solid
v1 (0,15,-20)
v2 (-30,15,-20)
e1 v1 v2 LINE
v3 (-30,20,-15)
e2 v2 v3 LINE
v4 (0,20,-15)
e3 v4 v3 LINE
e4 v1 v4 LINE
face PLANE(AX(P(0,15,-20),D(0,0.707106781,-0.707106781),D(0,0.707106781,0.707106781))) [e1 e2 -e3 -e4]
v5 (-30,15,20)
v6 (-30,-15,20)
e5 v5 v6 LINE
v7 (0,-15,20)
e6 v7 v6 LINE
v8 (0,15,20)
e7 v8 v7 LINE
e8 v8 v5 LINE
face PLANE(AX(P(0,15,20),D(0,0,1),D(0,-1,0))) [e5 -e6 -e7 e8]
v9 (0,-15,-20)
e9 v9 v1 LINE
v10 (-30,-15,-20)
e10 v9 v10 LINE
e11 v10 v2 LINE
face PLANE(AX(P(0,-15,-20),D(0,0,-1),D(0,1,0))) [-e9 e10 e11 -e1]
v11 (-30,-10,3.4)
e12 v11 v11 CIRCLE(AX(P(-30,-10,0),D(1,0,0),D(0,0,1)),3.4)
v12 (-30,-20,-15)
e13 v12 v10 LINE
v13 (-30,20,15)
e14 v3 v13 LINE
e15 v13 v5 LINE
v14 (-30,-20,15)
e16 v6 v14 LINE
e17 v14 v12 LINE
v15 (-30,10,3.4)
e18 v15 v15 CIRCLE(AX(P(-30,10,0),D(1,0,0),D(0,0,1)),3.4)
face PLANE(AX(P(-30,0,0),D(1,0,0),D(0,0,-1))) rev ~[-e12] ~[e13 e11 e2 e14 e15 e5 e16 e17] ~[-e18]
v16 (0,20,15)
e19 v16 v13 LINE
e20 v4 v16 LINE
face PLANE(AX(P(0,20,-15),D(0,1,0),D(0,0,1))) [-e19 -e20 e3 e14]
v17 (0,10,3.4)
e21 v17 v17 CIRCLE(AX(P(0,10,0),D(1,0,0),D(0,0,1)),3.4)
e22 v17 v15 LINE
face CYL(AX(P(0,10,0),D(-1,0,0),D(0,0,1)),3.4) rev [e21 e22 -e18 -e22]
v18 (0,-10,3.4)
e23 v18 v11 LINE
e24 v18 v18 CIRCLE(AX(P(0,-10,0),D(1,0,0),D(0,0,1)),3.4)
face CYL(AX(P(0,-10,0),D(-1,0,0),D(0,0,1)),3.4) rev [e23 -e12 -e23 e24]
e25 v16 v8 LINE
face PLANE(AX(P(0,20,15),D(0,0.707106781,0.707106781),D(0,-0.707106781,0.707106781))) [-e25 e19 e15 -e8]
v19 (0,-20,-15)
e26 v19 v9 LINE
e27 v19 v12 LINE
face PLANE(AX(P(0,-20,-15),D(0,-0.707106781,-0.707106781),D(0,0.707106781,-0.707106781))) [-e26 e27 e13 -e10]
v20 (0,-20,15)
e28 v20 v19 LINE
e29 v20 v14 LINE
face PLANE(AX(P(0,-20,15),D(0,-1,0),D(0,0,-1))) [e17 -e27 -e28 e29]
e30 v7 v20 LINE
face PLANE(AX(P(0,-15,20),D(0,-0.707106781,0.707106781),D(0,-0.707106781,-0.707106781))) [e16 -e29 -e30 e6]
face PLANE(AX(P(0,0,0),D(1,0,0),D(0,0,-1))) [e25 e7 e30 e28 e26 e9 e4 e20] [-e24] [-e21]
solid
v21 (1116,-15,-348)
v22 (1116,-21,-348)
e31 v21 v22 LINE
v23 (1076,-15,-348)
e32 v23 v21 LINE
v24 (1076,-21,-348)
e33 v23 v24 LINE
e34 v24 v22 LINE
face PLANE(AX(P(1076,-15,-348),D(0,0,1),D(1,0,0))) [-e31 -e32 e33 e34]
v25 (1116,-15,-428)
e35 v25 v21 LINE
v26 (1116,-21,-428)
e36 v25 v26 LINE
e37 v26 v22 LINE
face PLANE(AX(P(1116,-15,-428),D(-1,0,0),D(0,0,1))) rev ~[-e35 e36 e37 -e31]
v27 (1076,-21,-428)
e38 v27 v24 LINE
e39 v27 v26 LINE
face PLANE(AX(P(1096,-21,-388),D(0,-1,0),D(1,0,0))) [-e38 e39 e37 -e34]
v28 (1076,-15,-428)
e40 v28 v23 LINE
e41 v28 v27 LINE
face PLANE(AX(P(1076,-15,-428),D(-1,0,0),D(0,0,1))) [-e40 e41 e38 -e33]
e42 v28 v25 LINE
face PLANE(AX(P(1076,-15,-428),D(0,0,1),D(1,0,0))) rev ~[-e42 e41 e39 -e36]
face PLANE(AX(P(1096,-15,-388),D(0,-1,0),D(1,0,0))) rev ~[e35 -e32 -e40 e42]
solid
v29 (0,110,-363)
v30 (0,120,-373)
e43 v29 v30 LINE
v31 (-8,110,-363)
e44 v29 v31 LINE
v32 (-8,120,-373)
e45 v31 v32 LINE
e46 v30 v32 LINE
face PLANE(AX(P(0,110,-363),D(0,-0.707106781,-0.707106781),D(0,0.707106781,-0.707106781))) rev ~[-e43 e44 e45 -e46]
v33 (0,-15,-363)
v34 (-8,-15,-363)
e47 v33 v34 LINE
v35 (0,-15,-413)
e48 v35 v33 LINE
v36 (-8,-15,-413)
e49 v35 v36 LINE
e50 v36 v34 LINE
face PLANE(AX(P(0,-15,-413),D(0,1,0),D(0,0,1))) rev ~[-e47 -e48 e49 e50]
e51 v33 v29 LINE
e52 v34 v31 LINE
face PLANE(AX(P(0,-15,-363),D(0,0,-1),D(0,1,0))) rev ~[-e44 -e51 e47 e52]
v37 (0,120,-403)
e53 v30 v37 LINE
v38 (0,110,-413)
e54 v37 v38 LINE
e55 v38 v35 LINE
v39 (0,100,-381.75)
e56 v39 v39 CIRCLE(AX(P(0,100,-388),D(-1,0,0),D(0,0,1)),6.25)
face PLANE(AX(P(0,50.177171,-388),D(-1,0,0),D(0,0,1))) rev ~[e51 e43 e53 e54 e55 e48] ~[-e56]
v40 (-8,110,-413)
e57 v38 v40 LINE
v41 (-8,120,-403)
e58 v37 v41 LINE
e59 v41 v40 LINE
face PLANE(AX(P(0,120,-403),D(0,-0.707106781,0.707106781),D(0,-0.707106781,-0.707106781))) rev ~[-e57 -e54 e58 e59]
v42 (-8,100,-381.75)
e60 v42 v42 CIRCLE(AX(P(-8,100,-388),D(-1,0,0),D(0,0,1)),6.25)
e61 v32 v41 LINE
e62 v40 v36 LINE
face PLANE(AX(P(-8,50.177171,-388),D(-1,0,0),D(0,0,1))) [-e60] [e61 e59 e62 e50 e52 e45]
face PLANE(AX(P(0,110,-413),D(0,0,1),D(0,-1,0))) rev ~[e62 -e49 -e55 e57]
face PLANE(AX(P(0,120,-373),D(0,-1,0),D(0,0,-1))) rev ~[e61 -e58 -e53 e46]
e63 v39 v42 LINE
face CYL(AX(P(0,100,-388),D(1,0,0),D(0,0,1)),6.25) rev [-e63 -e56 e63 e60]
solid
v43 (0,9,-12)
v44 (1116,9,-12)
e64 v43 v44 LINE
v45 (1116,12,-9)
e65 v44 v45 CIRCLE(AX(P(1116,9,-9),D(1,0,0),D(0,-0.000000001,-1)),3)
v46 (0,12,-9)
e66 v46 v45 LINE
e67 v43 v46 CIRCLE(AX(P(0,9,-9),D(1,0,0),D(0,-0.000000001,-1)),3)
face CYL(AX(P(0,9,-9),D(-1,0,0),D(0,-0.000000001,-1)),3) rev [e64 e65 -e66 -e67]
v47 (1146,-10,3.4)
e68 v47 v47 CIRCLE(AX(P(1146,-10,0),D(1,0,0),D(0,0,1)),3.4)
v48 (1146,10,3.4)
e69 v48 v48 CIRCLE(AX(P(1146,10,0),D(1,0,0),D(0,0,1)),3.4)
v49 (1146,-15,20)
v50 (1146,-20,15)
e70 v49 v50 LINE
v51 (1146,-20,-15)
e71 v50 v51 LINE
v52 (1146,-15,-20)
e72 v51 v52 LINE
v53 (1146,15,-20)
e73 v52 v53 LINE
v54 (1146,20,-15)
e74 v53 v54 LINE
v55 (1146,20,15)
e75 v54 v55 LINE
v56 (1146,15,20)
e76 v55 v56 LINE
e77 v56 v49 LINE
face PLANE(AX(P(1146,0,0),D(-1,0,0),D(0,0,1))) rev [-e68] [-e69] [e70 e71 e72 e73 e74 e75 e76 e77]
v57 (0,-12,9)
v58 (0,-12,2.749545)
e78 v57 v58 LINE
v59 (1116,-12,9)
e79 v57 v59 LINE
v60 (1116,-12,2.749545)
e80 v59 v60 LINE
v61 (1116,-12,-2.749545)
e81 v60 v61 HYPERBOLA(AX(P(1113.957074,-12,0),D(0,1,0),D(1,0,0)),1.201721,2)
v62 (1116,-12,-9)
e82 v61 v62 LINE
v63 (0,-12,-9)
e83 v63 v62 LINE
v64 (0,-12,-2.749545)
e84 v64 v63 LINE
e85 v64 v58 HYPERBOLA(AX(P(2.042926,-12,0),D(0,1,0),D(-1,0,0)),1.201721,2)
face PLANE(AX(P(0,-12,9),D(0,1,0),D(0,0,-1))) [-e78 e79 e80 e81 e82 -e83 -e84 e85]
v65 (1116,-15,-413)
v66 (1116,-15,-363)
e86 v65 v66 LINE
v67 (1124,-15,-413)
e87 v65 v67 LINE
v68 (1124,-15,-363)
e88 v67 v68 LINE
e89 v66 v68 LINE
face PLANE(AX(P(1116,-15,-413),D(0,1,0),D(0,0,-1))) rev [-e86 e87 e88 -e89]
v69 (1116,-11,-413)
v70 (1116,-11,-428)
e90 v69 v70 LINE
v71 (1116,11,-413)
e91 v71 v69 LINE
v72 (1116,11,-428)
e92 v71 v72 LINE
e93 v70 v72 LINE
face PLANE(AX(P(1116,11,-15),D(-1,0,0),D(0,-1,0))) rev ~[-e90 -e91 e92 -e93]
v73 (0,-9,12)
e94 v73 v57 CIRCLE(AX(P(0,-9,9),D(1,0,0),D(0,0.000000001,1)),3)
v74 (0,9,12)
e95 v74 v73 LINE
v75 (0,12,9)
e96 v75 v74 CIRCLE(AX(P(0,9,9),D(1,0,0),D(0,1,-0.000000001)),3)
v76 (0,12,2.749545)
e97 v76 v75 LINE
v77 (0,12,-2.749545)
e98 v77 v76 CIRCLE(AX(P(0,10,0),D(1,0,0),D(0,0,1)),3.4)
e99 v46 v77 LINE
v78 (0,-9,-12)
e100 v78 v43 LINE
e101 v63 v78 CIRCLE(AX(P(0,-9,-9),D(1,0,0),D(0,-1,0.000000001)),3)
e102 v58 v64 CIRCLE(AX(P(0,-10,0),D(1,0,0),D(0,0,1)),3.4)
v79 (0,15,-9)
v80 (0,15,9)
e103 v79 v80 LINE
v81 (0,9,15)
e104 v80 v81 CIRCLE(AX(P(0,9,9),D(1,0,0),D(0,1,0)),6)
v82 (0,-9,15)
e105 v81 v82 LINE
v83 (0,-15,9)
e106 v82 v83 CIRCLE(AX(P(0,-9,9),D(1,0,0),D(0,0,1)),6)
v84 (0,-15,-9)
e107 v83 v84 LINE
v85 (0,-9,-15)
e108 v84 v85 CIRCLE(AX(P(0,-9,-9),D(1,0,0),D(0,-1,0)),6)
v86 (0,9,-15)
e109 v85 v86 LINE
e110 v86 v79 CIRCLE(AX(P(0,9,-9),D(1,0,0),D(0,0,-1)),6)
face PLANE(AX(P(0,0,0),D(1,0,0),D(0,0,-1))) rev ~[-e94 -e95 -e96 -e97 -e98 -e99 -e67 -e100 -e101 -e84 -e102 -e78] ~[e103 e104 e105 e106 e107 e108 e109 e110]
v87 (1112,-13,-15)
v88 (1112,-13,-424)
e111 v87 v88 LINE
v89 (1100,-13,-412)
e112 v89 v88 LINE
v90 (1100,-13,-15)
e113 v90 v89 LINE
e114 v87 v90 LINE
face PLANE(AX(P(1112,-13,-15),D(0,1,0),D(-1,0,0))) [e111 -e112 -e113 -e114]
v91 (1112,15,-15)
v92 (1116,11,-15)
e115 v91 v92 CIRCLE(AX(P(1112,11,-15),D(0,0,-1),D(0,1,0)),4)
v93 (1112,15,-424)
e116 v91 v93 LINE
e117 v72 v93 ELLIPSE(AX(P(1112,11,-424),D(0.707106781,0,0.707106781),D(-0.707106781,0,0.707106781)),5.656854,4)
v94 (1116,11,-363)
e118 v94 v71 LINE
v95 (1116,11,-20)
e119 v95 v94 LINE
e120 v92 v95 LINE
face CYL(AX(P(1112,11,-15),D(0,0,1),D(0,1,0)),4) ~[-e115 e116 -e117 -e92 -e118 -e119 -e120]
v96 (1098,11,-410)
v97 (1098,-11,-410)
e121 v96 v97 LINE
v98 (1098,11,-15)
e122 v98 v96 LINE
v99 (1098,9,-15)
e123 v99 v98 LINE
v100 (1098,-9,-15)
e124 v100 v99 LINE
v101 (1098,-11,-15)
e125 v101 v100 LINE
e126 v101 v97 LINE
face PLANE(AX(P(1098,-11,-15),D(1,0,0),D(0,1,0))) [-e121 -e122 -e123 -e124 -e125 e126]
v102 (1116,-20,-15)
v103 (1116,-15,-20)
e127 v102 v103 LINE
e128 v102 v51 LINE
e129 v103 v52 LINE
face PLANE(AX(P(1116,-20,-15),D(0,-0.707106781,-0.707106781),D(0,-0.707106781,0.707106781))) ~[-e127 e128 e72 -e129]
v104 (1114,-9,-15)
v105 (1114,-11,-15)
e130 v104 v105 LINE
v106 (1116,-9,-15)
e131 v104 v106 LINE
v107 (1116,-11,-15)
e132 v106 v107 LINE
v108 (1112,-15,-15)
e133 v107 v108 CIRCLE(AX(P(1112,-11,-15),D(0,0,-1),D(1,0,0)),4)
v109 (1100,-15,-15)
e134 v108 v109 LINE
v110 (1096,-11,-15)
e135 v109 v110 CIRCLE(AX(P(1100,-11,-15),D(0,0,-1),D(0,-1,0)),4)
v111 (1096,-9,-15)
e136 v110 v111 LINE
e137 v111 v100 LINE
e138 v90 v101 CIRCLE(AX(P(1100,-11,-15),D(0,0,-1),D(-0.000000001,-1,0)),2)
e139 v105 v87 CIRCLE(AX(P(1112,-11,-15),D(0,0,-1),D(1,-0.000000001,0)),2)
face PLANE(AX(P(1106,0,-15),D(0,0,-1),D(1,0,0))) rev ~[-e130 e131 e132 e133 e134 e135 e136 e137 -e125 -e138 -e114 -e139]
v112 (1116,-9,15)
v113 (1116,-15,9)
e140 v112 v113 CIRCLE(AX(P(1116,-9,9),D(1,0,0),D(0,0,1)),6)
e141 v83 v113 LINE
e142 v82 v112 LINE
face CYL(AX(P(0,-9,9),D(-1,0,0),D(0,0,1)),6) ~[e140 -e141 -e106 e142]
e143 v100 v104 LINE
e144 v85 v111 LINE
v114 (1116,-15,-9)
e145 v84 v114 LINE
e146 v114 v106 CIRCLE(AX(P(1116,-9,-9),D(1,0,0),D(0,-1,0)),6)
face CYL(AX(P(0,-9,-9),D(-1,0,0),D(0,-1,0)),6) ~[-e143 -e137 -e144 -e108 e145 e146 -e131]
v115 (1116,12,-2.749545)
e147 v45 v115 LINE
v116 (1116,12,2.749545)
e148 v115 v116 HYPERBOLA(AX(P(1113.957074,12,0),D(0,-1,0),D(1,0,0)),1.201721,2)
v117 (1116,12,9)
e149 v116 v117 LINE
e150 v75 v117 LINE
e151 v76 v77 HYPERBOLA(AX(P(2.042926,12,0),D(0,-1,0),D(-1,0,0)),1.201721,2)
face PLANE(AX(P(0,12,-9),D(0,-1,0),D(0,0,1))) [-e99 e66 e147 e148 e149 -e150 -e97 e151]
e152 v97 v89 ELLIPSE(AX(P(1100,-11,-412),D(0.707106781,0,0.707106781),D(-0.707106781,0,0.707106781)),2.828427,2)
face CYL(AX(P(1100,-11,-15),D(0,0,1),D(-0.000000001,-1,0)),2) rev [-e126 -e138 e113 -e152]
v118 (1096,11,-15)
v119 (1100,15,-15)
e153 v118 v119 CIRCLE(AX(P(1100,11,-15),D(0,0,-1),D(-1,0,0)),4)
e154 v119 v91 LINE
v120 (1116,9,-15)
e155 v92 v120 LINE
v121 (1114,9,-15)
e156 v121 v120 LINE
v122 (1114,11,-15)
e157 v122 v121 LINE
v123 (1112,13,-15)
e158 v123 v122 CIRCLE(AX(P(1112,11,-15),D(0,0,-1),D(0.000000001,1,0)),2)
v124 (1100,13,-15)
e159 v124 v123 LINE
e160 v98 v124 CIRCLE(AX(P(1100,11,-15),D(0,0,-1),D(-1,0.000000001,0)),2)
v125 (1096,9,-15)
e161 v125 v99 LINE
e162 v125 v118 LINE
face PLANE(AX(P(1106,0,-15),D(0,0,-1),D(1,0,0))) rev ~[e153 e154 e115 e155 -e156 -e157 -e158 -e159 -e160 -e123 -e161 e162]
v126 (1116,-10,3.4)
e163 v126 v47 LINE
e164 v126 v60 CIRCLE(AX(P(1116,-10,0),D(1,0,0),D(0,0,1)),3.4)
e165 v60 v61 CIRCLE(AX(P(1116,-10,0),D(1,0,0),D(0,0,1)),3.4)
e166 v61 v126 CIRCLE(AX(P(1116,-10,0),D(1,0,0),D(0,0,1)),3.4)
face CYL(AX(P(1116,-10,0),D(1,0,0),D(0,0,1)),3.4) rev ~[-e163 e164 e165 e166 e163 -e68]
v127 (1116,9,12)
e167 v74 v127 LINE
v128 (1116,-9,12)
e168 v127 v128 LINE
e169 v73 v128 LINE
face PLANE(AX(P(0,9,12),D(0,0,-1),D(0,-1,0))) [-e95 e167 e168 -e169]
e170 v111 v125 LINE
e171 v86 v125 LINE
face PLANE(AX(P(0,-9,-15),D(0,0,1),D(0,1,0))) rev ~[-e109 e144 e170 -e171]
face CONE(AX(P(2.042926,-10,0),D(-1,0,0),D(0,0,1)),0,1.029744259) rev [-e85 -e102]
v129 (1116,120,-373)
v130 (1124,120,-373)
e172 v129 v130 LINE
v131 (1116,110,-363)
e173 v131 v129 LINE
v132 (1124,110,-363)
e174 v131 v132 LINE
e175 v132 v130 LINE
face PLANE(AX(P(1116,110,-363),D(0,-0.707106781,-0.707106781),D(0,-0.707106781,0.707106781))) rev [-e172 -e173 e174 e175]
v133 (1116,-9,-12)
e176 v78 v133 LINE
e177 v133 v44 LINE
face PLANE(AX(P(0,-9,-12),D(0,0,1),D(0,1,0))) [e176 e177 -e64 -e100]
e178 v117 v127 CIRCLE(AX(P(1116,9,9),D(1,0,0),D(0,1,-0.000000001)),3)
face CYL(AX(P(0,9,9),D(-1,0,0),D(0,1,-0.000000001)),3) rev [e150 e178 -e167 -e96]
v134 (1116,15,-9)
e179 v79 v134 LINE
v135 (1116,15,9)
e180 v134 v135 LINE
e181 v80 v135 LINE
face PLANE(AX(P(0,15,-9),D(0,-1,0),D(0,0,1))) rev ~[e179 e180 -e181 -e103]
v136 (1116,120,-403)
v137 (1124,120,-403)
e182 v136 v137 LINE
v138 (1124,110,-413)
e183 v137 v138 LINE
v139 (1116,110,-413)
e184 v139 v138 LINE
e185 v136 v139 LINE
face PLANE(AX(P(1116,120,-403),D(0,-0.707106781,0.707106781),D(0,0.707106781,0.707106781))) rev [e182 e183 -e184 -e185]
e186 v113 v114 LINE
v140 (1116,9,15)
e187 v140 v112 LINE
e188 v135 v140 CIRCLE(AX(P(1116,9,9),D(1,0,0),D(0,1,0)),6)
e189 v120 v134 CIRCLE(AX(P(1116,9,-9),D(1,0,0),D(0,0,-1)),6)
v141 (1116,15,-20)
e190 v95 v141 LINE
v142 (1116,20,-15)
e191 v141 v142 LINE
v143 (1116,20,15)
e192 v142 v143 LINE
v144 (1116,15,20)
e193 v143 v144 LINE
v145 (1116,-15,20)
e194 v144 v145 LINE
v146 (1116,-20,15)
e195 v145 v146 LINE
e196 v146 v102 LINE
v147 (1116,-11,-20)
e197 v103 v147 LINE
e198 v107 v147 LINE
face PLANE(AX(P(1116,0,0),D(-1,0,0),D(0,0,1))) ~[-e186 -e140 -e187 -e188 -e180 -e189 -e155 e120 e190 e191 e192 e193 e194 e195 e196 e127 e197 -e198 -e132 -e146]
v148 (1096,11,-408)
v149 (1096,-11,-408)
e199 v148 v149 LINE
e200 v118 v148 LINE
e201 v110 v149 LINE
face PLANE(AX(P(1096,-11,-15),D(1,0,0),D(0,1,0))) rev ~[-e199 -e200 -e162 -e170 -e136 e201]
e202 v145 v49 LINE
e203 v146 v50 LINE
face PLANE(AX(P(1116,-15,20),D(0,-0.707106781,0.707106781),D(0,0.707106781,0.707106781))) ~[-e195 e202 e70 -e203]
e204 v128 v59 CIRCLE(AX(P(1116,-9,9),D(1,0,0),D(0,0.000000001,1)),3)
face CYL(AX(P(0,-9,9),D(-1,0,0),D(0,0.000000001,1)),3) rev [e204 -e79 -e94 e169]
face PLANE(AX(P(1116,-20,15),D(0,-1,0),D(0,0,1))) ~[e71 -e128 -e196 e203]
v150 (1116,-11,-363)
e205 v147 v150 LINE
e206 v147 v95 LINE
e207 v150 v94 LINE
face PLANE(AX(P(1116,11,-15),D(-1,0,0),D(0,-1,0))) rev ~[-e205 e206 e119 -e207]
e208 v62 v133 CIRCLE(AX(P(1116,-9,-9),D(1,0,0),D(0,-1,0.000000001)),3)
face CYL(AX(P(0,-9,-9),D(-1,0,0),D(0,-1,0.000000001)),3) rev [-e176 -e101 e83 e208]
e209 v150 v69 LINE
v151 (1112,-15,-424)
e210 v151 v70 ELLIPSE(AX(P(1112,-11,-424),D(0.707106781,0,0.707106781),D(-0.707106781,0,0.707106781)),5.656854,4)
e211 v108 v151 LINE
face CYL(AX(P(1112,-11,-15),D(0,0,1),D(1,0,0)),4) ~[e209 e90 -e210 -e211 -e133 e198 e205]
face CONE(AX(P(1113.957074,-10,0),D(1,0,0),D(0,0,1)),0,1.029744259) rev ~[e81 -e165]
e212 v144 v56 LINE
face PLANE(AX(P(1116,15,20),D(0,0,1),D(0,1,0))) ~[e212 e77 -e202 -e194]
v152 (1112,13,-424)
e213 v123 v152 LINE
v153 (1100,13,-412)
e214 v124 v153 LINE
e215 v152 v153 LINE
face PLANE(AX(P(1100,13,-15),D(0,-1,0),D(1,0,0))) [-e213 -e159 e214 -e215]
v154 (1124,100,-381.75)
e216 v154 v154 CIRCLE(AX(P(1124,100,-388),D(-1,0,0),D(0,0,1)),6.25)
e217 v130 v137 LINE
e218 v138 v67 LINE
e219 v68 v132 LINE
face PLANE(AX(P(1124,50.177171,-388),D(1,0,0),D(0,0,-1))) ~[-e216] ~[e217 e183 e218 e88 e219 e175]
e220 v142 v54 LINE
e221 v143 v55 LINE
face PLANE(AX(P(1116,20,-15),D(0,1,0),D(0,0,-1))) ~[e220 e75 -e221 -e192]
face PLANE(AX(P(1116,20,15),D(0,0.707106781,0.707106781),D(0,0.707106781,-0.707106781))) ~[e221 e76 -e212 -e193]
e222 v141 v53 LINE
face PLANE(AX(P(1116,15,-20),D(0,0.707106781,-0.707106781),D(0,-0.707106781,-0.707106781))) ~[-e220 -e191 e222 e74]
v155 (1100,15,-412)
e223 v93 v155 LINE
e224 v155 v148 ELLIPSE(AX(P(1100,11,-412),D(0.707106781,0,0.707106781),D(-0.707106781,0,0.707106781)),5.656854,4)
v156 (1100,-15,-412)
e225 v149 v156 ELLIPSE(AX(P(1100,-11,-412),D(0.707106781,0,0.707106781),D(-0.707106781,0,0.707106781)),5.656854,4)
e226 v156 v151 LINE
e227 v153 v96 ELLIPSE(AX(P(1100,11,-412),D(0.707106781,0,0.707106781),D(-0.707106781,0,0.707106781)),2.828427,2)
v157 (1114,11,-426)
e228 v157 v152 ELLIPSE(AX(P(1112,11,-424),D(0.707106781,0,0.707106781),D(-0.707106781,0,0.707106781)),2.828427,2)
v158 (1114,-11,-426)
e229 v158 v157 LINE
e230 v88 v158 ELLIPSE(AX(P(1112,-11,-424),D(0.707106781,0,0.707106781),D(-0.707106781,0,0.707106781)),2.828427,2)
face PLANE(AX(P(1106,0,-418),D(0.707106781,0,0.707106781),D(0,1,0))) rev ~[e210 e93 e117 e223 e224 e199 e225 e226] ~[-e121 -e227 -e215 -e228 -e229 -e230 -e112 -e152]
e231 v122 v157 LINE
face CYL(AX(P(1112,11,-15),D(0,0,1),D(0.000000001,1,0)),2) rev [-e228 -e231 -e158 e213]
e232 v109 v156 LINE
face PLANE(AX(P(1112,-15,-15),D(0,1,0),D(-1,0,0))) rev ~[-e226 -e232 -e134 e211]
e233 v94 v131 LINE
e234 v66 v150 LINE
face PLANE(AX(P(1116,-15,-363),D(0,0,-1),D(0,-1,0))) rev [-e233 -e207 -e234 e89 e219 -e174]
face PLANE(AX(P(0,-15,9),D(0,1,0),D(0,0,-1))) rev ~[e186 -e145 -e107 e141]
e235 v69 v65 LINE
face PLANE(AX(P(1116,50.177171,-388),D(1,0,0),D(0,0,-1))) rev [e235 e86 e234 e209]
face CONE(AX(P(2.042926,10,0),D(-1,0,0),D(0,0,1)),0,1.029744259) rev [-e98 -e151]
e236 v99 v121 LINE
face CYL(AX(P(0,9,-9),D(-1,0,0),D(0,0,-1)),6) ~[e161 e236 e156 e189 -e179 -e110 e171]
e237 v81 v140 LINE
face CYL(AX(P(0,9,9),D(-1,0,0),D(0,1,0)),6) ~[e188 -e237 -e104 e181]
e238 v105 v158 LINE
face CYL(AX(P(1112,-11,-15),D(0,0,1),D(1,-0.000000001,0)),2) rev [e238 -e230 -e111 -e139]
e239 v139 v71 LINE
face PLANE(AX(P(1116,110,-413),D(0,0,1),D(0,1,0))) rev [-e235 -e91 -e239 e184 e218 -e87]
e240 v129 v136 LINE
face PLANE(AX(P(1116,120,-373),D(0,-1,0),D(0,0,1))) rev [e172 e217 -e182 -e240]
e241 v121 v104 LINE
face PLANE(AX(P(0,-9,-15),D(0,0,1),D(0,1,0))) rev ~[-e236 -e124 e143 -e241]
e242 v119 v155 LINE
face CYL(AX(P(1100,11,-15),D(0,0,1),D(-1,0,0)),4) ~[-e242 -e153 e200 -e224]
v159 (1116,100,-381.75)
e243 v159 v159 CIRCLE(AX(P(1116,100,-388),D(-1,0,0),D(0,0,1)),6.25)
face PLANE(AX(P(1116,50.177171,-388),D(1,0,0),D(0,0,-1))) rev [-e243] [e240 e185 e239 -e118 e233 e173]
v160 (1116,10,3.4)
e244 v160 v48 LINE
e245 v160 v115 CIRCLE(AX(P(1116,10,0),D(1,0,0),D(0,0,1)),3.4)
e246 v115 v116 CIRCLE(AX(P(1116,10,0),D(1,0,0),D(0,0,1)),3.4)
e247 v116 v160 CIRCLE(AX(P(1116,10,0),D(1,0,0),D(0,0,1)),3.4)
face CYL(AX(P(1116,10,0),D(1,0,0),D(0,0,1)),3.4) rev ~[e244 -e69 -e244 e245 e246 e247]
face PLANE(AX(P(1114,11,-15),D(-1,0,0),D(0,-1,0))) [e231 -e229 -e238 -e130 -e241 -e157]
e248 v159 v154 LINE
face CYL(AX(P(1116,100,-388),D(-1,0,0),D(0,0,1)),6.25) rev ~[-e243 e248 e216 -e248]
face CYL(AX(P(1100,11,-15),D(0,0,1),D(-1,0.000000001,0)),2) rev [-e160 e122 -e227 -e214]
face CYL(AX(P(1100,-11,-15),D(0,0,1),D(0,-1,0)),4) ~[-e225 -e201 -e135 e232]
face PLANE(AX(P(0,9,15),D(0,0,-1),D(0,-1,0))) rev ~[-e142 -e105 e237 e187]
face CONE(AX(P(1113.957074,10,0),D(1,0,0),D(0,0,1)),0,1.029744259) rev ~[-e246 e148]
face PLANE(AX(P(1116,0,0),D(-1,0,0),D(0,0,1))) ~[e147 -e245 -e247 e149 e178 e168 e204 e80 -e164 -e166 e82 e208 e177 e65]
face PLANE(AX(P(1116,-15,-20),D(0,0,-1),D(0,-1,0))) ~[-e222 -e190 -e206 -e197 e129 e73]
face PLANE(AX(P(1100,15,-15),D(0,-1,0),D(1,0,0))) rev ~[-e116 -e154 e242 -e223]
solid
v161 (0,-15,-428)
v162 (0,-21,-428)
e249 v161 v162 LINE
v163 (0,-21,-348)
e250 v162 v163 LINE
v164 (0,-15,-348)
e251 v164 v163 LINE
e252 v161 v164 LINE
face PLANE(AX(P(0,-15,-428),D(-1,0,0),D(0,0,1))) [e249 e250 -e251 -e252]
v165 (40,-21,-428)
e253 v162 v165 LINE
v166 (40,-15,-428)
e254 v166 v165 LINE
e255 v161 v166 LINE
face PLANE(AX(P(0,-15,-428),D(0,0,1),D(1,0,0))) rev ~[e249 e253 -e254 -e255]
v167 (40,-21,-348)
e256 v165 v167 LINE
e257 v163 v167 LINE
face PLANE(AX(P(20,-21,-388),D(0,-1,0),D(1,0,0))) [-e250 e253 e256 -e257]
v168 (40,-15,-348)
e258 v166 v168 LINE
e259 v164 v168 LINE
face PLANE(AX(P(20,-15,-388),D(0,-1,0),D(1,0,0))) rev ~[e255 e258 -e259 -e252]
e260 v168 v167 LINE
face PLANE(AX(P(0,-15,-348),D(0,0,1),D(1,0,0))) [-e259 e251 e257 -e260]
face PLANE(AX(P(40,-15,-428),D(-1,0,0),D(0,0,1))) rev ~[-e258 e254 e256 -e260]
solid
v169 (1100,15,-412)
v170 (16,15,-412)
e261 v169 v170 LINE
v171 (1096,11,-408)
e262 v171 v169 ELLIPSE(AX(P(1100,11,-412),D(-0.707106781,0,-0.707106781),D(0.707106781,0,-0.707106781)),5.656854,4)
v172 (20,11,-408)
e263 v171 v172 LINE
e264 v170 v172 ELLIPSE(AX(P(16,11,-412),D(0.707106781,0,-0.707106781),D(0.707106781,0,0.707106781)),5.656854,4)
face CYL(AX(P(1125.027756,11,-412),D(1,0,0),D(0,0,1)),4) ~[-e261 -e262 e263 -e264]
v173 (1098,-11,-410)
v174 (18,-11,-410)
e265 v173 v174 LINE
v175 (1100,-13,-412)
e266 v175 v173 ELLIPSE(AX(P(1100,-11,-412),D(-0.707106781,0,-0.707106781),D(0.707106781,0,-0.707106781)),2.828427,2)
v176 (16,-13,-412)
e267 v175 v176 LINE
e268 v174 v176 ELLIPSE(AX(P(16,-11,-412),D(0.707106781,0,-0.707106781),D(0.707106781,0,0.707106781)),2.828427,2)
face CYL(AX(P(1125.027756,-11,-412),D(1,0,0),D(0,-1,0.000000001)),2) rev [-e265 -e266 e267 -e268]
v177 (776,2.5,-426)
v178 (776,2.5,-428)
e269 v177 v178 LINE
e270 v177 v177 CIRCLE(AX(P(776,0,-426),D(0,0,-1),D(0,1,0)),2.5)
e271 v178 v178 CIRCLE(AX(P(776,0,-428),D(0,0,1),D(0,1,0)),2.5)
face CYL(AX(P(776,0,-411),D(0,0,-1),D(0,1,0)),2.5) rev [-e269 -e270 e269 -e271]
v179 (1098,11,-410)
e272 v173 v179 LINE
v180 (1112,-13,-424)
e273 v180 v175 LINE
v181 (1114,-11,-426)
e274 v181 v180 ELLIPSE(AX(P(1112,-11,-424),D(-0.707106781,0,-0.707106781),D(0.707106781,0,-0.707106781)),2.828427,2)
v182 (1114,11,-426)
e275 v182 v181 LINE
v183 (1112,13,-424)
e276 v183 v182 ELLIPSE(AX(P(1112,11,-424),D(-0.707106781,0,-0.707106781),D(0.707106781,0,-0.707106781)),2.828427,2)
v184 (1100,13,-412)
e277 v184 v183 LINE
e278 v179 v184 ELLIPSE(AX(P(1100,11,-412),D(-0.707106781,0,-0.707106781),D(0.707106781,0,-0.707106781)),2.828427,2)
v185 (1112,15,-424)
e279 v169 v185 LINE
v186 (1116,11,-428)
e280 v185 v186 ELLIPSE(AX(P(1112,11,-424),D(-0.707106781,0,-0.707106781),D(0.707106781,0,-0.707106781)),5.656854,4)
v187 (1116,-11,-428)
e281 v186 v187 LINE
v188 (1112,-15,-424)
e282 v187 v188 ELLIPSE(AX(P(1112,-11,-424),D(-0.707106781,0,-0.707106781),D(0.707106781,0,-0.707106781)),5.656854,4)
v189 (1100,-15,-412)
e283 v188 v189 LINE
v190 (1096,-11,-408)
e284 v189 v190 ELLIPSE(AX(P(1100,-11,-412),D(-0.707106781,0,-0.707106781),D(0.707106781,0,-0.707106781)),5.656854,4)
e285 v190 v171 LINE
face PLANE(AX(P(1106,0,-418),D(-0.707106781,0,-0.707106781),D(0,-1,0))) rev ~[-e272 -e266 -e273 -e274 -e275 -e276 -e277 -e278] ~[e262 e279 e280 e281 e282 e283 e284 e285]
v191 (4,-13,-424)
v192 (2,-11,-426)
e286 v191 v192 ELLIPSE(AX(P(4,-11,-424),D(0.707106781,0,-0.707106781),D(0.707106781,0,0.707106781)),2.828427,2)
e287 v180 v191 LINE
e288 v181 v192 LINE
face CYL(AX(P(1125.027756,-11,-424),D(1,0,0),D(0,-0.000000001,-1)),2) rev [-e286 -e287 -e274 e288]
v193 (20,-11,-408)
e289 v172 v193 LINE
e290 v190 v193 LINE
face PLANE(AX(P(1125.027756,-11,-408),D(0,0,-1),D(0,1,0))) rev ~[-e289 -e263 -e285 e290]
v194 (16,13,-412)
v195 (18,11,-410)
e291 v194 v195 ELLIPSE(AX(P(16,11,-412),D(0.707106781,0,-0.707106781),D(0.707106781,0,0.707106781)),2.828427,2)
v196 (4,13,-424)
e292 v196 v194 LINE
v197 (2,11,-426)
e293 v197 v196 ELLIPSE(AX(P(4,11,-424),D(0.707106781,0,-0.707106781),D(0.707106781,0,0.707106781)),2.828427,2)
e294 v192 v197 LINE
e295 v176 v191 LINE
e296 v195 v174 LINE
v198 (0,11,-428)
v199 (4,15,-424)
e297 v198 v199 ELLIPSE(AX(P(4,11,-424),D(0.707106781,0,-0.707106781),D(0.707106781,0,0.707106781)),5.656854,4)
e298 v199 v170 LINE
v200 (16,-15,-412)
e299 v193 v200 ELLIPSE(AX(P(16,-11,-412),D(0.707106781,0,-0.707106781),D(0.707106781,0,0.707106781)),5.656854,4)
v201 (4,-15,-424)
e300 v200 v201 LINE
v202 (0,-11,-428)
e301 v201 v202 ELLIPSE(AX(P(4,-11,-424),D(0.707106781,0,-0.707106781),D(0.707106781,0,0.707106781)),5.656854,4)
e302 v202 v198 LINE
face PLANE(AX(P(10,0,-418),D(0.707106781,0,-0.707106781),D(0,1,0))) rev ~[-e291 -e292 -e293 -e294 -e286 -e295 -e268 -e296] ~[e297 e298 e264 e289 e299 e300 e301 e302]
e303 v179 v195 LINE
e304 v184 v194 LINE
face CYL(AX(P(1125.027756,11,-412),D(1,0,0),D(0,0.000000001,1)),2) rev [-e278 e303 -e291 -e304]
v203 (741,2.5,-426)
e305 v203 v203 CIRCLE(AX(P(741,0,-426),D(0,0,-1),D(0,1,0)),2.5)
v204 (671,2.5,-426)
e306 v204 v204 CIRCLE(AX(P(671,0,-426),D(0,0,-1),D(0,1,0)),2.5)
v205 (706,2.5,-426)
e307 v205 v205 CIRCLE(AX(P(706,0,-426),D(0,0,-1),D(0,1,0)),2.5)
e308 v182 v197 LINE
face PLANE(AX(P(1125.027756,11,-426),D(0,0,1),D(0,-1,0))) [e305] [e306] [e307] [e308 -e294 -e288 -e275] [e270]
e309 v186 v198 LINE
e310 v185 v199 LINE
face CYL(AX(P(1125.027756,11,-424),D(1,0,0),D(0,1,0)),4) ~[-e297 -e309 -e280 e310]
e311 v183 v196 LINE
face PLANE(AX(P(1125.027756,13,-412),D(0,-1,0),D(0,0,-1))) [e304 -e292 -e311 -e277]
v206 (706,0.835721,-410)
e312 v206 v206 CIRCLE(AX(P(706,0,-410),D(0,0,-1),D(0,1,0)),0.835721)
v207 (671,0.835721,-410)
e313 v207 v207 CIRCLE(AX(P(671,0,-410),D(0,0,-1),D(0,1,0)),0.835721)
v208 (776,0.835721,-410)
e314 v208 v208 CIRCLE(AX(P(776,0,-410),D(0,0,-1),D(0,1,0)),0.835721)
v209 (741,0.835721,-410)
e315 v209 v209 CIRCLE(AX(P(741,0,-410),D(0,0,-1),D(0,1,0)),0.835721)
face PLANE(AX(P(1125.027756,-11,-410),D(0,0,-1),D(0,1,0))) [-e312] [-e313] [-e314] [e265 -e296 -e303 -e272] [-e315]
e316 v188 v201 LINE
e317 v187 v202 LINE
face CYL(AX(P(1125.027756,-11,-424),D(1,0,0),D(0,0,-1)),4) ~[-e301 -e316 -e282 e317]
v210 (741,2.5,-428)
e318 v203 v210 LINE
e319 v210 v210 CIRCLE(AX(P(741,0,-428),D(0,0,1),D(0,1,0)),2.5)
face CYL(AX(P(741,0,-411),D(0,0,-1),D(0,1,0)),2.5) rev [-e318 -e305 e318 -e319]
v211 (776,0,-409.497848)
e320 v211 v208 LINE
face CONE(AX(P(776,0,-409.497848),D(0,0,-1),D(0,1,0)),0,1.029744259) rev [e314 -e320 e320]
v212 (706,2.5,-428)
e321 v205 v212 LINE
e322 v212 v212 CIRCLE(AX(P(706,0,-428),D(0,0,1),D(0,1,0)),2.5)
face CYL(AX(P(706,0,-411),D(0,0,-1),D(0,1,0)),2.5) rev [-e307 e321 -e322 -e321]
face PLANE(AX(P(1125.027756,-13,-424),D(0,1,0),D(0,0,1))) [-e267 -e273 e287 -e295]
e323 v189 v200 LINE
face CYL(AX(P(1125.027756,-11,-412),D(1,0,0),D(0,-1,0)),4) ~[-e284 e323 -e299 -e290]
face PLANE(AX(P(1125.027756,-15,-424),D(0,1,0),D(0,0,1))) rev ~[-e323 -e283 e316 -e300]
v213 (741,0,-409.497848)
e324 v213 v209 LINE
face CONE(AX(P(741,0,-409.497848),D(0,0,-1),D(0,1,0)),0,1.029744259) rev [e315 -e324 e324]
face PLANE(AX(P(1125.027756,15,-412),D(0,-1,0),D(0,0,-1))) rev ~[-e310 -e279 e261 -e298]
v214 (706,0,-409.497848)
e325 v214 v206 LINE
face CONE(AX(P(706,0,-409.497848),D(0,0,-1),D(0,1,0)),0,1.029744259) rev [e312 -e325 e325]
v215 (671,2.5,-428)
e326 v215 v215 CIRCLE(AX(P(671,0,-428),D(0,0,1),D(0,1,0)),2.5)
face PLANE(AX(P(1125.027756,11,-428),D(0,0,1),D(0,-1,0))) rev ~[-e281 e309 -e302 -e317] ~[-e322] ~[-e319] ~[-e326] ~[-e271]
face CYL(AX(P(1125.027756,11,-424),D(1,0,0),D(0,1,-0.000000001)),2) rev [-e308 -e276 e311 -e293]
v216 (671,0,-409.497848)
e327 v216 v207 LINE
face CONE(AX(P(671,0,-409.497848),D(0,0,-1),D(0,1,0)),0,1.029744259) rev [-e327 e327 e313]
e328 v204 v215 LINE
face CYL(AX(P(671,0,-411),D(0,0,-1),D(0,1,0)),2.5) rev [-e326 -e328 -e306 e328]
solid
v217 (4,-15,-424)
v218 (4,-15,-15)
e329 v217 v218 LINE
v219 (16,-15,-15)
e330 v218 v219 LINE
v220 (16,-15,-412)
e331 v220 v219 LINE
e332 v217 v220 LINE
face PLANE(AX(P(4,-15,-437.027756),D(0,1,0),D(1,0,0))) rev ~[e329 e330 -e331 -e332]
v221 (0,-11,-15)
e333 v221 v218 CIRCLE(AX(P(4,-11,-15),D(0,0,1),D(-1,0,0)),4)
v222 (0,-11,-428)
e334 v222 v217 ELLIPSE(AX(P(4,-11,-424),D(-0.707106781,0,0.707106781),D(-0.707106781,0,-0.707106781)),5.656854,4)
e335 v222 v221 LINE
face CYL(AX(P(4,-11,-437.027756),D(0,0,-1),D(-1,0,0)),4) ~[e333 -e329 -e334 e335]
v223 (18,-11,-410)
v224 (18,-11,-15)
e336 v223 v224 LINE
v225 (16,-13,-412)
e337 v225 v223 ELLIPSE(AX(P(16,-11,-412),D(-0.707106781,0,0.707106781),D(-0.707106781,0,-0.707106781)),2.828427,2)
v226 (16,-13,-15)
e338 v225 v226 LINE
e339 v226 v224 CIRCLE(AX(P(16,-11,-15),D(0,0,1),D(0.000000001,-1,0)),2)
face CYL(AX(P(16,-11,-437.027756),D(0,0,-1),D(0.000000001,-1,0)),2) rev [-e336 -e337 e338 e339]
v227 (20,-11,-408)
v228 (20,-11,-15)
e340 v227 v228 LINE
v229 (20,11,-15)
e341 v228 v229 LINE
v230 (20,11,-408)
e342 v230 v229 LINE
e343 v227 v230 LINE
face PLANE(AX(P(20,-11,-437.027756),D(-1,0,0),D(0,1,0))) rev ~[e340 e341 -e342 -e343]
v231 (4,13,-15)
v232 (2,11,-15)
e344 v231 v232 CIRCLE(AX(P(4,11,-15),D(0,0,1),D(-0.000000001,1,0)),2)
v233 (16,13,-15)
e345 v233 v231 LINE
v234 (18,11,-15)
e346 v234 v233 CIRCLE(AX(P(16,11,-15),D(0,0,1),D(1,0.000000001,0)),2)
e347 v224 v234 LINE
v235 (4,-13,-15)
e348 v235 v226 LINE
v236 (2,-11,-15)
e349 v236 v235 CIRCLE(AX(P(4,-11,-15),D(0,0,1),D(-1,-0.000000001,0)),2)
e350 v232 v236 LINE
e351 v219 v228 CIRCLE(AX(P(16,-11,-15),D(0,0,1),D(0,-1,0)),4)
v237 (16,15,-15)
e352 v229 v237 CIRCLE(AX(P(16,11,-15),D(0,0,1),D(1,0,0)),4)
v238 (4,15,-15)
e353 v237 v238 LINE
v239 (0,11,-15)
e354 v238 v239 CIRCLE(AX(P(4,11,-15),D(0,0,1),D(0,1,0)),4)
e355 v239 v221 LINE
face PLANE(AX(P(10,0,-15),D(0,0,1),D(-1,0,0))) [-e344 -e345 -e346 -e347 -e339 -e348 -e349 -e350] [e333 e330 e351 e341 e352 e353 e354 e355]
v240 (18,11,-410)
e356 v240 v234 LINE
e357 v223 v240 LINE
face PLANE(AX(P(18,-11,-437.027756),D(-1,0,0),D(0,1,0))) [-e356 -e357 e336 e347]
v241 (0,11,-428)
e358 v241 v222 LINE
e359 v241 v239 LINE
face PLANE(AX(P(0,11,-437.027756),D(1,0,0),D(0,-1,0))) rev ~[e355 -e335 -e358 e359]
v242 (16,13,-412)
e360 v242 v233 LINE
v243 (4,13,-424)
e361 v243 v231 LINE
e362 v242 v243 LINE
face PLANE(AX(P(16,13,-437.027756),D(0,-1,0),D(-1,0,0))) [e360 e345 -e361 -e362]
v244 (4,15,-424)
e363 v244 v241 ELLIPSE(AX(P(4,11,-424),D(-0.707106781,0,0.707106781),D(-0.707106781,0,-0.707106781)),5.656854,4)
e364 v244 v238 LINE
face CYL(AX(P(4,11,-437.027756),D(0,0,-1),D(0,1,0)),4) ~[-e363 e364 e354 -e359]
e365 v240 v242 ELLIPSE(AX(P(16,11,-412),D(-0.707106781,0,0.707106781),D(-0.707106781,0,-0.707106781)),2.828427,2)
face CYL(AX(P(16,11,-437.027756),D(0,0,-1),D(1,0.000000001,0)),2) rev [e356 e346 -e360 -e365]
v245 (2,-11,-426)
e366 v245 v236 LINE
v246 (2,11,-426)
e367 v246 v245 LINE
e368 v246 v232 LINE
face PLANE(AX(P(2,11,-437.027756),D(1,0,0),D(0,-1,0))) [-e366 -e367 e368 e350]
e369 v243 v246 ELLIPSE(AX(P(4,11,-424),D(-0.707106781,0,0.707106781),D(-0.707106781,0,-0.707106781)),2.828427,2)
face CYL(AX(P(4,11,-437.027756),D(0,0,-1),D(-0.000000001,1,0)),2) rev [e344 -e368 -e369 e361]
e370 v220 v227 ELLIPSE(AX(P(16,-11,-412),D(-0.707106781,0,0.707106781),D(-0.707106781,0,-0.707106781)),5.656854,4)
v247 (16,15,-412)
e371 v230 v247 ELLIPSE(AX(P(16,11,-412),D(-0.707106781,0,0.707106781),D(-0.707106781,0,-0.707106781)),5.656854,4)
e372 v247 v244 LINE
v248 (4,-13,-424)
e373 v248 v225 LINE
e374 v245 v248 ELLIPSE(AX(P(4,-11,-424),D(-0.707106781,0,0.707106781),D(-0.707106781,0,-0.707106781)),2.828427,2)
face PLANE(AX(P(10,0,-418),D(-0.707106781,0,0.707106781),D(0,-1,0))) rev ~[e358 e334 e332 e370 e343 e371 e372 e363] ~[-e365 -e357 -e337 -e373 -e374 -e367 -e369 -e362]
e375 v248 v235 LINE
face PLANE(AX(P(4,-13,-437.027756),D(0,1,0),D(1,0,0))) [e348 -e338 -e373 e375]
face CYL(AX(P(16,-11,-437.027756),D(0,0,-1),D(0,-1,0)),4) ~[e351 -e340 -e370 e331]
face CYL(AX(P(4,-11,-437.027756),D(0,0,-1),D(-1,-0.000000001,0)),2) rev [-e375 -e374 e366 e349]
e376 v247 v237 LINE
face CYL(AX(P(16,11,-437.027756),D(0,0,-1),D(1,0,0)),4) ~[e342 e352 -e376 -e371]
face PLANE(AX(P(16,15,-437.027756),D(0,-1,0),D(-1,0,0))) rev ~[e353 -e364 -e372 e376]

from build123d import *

# Parameters (mm, degrees)
COLD_FORMED_HOLLOW_SQUARE_STEEL_GB_T_67_DEPTH = 1116
COLD_FORMED_HOLLOW_RECTANGULAR_STEEL_GB_DEPTH = 422.027756377
COLD_FORMED_HOLLOW_RECTANGULAR_STEEL_3_DEPTH  = 1134.055512755
COLD_FORMED_HOLLOW_RECTANGULAR_STEEL_5_DEPTH  = 422.027756377
BOSS_EXTRUDE1_DEPTH                           = 30
SKETCH5_R                                     = 1.70107459
CUT_EXTRUDE1_DEPTH                            = 30
M8_TAPPED_HOLE1_AT_2_COUNT                    = 2
M8_TAPPED_HOLE1_AT_2_PITCH                    = 20
SKETCH7_W                                     = 40
SKETCH7_H                                     = 80
BOSS_EXTRUDE2_DEPTH                           = 6
BOSS_EXTRUDE2_2_DEPTH                         = 6
SKETCH9_R                                     = 6.25
BOSS_EXTRUDE3_DEPTH                           = 8
SKETCH10_R                                    = 2
CUT_EXTRUDE2_DEPTH                            = 8
M6_TAPPED_HOLE1_AT_2_COUNT                    = 2
M6_TAPPED_HOLE1_AT_2_PITCH                    = 35
M6_TAPPED_HOLE1_AT_3_COUNT                    = 2
M6_TAPPED_HOLE1_AT_3_PITCH                    = 70
M6_TAPPED_HOLE1_AT_4_COUNT                    = 2
M6_TAPPED_HOLE1_AT_4_PITCH                    = 105


with BuildPart() as part:
    # Sketch11 → Cold-formed hollow square steel (GB/T 6728-2002) 30×3(1) (new body)
    with BuildSketch(Plane(origin=(0, 0, 0), x_dir=(0, 0, -1), z_dir=(1, 0, 0))):
        with BuildLine():
            Line((-9, -15), (9, -15))
            ThreePointArc((9, -15), (13.242640687, -13.242640687), (15, -9))
            Line((15, -9), (15, 9))
            ThreePointArc((15, 9), (13.242640687, 13.242640687), (9, 15))
            Line((9, 15), (-9, 15))
            ThreePointArc((-9, 15), (-13.242640687, 13.242640687), (-15, 9))
            Line((-15, 9), (-15, -9))
            ThreePointArc((-15, -9), (-13.242640687, -13.242640687), (-9, -15))
        make_face()
        with BuildLine():
            Line((-9, -12), (9, -12))
            ThreePointArc((9, -12), (11.121320344, -11.121320344), (12, -9))
            Line((12, -9), (12, 9))
            ThreePointArc((12, 9), (11.121320344, 11.121320344), (9, 12))
            Line((9, 12), (-9, 12))
            ThreePointArc((-9, 12), (-11.121320344, 11.121320344), (-12, 9))
            Line((-12, 9), (-12, -9))
            ThreePointArc((-12, -9), (-11.121320344, -11.121320344), (-9, -12))
        make_face(mode=Mode.SUBTRACT)
    extrude(amount=COLD_FORMED_HOLLOW_SQUARE_STEEL_GB_T_67_DEPTH)


with BuildPart() as body_2:
    # Sketch1 → Cold-formed hollow rectangular steel (GB/T 6728-2002) 30×20×2(1) (new body)
    with BuildSketch(Plane(origin=(1106, 0, -15), x_dir=(1, 0, 0), z_dir=(0, 0, -1))):
        with BuildLine():
            Line((-6, -15), (6, -15))
            ThreePointArc((6, -15), (8.828427125, -13.828427125), (10, -11))
            Line((10, -11), (10, 11))
            ThreePointArc((10, 11), (8.828427125, 13.828427125), (6, 15))
            Line((6, 15), (-6, 15))
            ThreePointArc((-6, 15), (-8.828427125, 13.828427125), (-10, 11))
            Line((-10, 11), (-10, -11))
            ThreePointArc((-10, -11), (-8.828427125, -13.828427125), (-6, -15))
        make_face()
        with BuildLine():
            Line((-6, -13), (6, -13))
            ThreePointArc((6, -13), (7.414213562, -12.414213562), (8, -11))
            Line((8, -11), (8, 11))
            ThreePointArc((8, 11), (7.414213562, 12.414213562), (6, 13))
            Line((6, 13), (-6, 13))
            ThreePointArc((-6, 13), (-7.414213562, 12.414213562), (-8, 11))
            Line((-8, 11), (-8, -11))
            ThreePointArc((-8, -11), (-7.414213562, -12.414213562), (-6, -13))
        make_face(mode=Mode.SUBTRACT)
    extrude(amount=COLD_FORMED_HOLLOW_RECTANGULAR_STEEL_GB_DEPTH)

    # Cold-formed hollow rectangular steel 2
    split(bisect_by=Plane(origin=(1106, 0, -418), x_dir=(0, 1, 0), z_dir=(0.707106781, 0, 0.707106781)), keep=Keep.TOP)


with BuildPart() as body_3:
    # Sketch1 on segment 2 (carried to segment 2) → Cold-formed hollow rectangular steel 3 (new body)
    with BuildSketch(Plane(origin=(1125.027756377, 0, -418), x_dir=(0, 0, -1), z_dir=(-1, 0, 0))):
        with BuildLine():
            Line((-6, -15), (6, -15))
            ThreePointArc((6, -15), (8.828427125, -13.828427125), (10, -11))
            Line((10, -11), (10, 11))
            ThreePointArc((10, 11), (8.828427125, 13.828427125), (6, 15))
            Line((6, 15), (-6, 15))
            ThreePointArc((-6, 15), (-8.828427125, 13.828427125), (-10, 11))
            Line((-10, 11), (-10, -11))
            ThreePointArc((-10, -11), (-8.828427125, -13.828427125), (-6, -15))
        make_face()
        with BuildLine():
            Line((-6, -13), (6, -13))
            ThreePointArc((6, -13), (7.414213562, -12.414213562), (8, -11))
            Line((8, -11), (8, 11))
            ThreePointArc((8, 11), (7.414213562, 12.414213562), (6, 13))
            Line((6, 13), (-6, 13))
            ThreePointArc((-6, 13), (-7.414213562, 12.414213562), (-8, 11))
            Line((-8, 11), (-8, -11))
            ThreePointArc((-8, -11), (-7.414213562, -12.414213562), (-6, -13))
        make_face(mode=Mode.SUBTRACT)
    extrude(amount=COLD_FORMED_HOLLOW_RECTANGULAR_STEEL_3_DEPTH)

    # Cold-formed hollow rectangular steel 3 m
    split(bisect_by=Plane(origin=(10, 0, -418), x_dir=(0, 1, 0), z_dir=(0.707106781, 0, -0.707106781)), keep=Keep.TOP)

    # Cold-formed hollow rectangular steel 4
    split(bisect_by=Plane(origin=(1106, 0, -418), x_dir=(0, -1, 0), z_dir=(-0.707106781, 0, -0.707106781)), keep=Keep.TOP)

    # Sketch10 → Cut-Extrude2 (cut)
    with BuildSketch(Plane(origin=(0, 0, -428), x_dir=(-1, 0, 0), z_dir=(0, 0, -1))):
        with Locations(Location((-776, 0, 0), (0, 0, 90))):
            Circle(SKETCH10_R)
        with Locations(Location((-741, 0, 0), (0, 0, 90))):
            Circle(SKETCH10_R)
        with Locations(Location((-706, 0, 0), (0, 0, 90))):
            Circle(SKETCH10_R)
        with Locations(Location((-671, 0, 0), (0, 0, 90))):
            Circle(SKETCH10_R)
    extrude(amount=-CUT_EXTRUDE2_DEPTH, mode=Mode.SUBTRACT)

    # 草图11 → M6 Tapped Hole1 (revolve, cut)
    with BuildSketch(Plane(origin=(671, 0, -428), x_dir=(0, 1, 0), z_dir=(1, 0, 0))):
        Polygon((0, 0), (0, 18.502151548), (2.5, 17), (2.5, 0), align=None)
    m6_tapped_hole1 = revolve(axis=Axis((671, 0, -434.35), (0, 0, 1)), mode=Mode.SUBTRACT)

    # M6 Tapped Hole1 at 2: M6 Tapped Hole1 ×2
    with Locations(*[(i * M6_TAPPED_HOLE1_AT_2_PITCH, 0, 0) for i in range(1, M6_TAPPED_HOLE1_AT_2_COUNT)]):
        add(m6_tapped_hole1, mode=Mode.SUBTRACT)

    # M6 Tapped Hole1 at 3: M6 Tapped Hole1 ×2
    with Locations(*[(i * M6_TAPPED_HOLE1_AT_3_PITCH, 0, 0) for i in range(1, M6_TAPPED_HOLE1_AT_3_COUNT)]):
        add(m6_tapped_hole1, mode=Mode.SUBTRACT)

    # M6 Tapped Hole1 at 4: M6 Tapped Hole1 ×2
    with Locations(*[(i * M6_TAPPED_HOLE1_AT_4_PITCH, 0, 0) for i in range(1, M6_TAPPED_HOLE1_AT_4_COUNT)]):
        add(m6_tapped_hole1, mode=Mode.SUBTRACT)


with BuildPart() as body_4:
    # Sketch1 on segment 3 (carried to segment 3) → Cold-formed hollow rectangular steel 5 (new body)
    with BuildSketch(Plane(origin=(10, 0, -437.027756377), x_dir=(-1, 0, 0), z_dir=(0, 0, 1))):
        with BuildLine():
            Line((-6, -15), (6, -15))
            ThreePointArc((6, -15), (8.828427125, -13.828427125), (10, -11))
            Line((10, -11), (10, 11))
            ThreePointArc((10, 11), (8.828427125, 13.828427125), (6, 15))
            Line((6, 15), (-6, 15))
            ThreePointArc((-6, 15), (-8.828427125, 13.828427125), (-10, 11))
            Line((-10, 11), (-10, -11))
            ThreePointArc((-10, -11), (-8.828427125, -13.828427125), (-6, -15))
        make_face()
        with BuildLine():
            Line((-6, -13), (6, -13))
            ThreePointArc((6, -13), (7.414213562, -12.414213562), (8, -11))
            Line((8, -11), (8, 11))
            ThreePointArc((8, 11), (7.414213562, 12.414213562), (6, 13))
            Line((6, 13), (-6, 13))
            ThreePointArc((-6, 13), (-7.414213562, 12.414213562), (-8, 11))
            Line((-8, 11), (-8, -11))
            ThreePointArc((-8, -11), (-7.414213562, -12.414213562), (-6, -13))
        make_face(mode=Mode.SUBTRACT)
    extrude(amount=COLD_FORMED_HOLLOW_RECTANGULAR_STEEL_5_DEPTH)

    # Cold-formed hollow rectangular steel 5 m
    split(bisect_by=Plane(origin=(10, 0, -418), x_dir=(0, -1, 0), z_dir=(-0.707106781, 0, 0.707106781)), keep=Keep.TOP)


with BuildPart() as body_5:
    # Sketch4 → Boss-Extrude1 (new body)
    with BuildSketch(Plane.ZY):
        Polygon((-20, 15), (-15, 20), (15, 20), (20, 15), (20, -15), (15, -20), (-15, -20), (-20, -15), align=None)
    boss_extrude1 = extrude(amount=BOSS_EXTRUDE1_DEPTH)

    # Sketch5 → Cut-Extrude1 (cut)
    with BuildSketch(Plane.ZY.offset(30)):
        with Locations((0, 10)):
            Circle(SKETCH5_R)
        with Locations((0, -10)):
            Circle(SKETCH5_R)
    cut_extrude1 = extrude(amount=-CUT_EXTRUDE1_DEPTH, mode=Mode.SUBTRACT)


with BuildPart() as m8_tapped_hole1_tool:
    # Sketch6 → M8 Tapped Hole1 (revolve)
    with BuildSketch(Plane(origin=(-30, 10, 0), x_dir=(0, 0, 1), z_dir=(0, 1, 0))):
        Polygon((0, 0), (0, 32.042926105), (3.4, 30), (3.4, 0), align=None)
    m8_tapped_hole1 = revolve(axis=Axis((-36.35, 10, 0), (1, 0, 0)))


with BuildPart() as part_1:
    add(part.part)

    # M8 Tapped Hole1: cut by m8_tapped_hole1_tool
    add(m8_tapped_hole1_tool.part, mode=Mode.SUBTRACT)


with BuildPart() as body_5_1:
    add(body_5.part)

    # M8 Tapped Hole1: cut by m8_tapped_hole1_tool
    add(m8_tapped_hole1_tool.part, mode=Mode.SUBTRACT)


with BuildPart() as m8_tapped_hole1_at_2_tool:
    # M8 Tapped Hole1 at 2: M8 Tapped Hole1 ×2
    with Locations(*[(0, -i * M8_TAPPED_HOLE1_AT_2_PITCH, 0) for i in range(1, M8_TAPPED_HOLE1_AT_2_COUNT)]):
        add(m8_tapped_hole1)


with BuildPart() as part_2:
    add(part_1.part)

    # M8 Tapped Hole1 at 2: cut by m8_tapped_hole1_at_2_tool
    add(m8_tapped_hole1_at_2_tool.part, mode=Mode.SUBTRACT)


with BuildPart() as body_5_2:
    add(body_5_1.part)

    # M8 Tapped Hole1 at 2: cut by m8_tapped_hole1_at_2_tool
    add(m8_tapped_hole1_at_2_tool.part, mode=Mode.SUBTRACT)


with BuildPart() as body_6:
    # Sketch7 → Boss-Extrude2 (new body)
    with BuildSketch(Plane.XZ.offset(15)):
        with Locations((1096, -388)):
            Rectangle(SKETCH7_W, SKETCH7_H)
    extrude(amount=BOSS_EXTRUDE2_DEPTH)


with BuildPart() as body_7:
    # Sketch7 → Boss-Extrude2 2 (new body)
    with BuildSketch(Plane.XZ.offset(15)):
        with Locations((20, -388)):
            Rectangle(SKETCH7_W, SKETCH7_H)
    extrude(amount=BOSS_EXTRUDE2_2_DEPTH)


with BuildPart() as body_8:
    # Sketch9 → Boss-Extrude3 (new body)
    with BuildSketch(Plane.ZY):
        Polygon((-413, -15), (-363, -15), (-363, 110), (-373, 120), (-403, 120), (-413, 110), align=None)
        with Locations((-388, 100)):
            Circle(SKETCH9_R, mode=Mode.SUBTRACT)
    boss_extrude3 = extrude(amount=BOSS_EXTRUDE3_DEPTH)


with BuildPart() as part_3:
    add(part_2.part)

    add(body_2.part)  # Mirror1 merges body 2
    # Mirror1: Boss-Extrude1, Cut-Extrude1, M8 Tapped Hole1, Boss-Extrude3 across plane
    add(boss_extrude1.mirror(Plane.ZY.offset(-558)))
    add(cut_extrude1.mirror(Plane.ZY.offset(-558)), mode=Mode.SUBTRACT)
    add(m8_tapped_hole1.mirror(Plane.ZY.offset(-558)), mode=Mode.SUBTRACT)
    add(boss_extrude3.mirror(Plane.ZY.offset(-558)))

    # Mirror1 copy 1 sketch → Mirror1 copy 1 (revolve, cut)
    with BuildSketch(Plane(origin=(1146, -10, 0), x_dir=(0, 0, 1), z_dir=(0, 1, 0))):
        Polygon((0, 0), (0, -32.042926105), (3.4, -30), (3.4, 0), align=None)
    revolve(axis=Axis((1152.35, -10, 0), (1, 0, 0)), mode=Mode.SUBTRACT)


solid = Compound([body_3.part, body_4.part, body_5_2.part, body_6.part, body_7.part, body_8.part, part_3.part])
